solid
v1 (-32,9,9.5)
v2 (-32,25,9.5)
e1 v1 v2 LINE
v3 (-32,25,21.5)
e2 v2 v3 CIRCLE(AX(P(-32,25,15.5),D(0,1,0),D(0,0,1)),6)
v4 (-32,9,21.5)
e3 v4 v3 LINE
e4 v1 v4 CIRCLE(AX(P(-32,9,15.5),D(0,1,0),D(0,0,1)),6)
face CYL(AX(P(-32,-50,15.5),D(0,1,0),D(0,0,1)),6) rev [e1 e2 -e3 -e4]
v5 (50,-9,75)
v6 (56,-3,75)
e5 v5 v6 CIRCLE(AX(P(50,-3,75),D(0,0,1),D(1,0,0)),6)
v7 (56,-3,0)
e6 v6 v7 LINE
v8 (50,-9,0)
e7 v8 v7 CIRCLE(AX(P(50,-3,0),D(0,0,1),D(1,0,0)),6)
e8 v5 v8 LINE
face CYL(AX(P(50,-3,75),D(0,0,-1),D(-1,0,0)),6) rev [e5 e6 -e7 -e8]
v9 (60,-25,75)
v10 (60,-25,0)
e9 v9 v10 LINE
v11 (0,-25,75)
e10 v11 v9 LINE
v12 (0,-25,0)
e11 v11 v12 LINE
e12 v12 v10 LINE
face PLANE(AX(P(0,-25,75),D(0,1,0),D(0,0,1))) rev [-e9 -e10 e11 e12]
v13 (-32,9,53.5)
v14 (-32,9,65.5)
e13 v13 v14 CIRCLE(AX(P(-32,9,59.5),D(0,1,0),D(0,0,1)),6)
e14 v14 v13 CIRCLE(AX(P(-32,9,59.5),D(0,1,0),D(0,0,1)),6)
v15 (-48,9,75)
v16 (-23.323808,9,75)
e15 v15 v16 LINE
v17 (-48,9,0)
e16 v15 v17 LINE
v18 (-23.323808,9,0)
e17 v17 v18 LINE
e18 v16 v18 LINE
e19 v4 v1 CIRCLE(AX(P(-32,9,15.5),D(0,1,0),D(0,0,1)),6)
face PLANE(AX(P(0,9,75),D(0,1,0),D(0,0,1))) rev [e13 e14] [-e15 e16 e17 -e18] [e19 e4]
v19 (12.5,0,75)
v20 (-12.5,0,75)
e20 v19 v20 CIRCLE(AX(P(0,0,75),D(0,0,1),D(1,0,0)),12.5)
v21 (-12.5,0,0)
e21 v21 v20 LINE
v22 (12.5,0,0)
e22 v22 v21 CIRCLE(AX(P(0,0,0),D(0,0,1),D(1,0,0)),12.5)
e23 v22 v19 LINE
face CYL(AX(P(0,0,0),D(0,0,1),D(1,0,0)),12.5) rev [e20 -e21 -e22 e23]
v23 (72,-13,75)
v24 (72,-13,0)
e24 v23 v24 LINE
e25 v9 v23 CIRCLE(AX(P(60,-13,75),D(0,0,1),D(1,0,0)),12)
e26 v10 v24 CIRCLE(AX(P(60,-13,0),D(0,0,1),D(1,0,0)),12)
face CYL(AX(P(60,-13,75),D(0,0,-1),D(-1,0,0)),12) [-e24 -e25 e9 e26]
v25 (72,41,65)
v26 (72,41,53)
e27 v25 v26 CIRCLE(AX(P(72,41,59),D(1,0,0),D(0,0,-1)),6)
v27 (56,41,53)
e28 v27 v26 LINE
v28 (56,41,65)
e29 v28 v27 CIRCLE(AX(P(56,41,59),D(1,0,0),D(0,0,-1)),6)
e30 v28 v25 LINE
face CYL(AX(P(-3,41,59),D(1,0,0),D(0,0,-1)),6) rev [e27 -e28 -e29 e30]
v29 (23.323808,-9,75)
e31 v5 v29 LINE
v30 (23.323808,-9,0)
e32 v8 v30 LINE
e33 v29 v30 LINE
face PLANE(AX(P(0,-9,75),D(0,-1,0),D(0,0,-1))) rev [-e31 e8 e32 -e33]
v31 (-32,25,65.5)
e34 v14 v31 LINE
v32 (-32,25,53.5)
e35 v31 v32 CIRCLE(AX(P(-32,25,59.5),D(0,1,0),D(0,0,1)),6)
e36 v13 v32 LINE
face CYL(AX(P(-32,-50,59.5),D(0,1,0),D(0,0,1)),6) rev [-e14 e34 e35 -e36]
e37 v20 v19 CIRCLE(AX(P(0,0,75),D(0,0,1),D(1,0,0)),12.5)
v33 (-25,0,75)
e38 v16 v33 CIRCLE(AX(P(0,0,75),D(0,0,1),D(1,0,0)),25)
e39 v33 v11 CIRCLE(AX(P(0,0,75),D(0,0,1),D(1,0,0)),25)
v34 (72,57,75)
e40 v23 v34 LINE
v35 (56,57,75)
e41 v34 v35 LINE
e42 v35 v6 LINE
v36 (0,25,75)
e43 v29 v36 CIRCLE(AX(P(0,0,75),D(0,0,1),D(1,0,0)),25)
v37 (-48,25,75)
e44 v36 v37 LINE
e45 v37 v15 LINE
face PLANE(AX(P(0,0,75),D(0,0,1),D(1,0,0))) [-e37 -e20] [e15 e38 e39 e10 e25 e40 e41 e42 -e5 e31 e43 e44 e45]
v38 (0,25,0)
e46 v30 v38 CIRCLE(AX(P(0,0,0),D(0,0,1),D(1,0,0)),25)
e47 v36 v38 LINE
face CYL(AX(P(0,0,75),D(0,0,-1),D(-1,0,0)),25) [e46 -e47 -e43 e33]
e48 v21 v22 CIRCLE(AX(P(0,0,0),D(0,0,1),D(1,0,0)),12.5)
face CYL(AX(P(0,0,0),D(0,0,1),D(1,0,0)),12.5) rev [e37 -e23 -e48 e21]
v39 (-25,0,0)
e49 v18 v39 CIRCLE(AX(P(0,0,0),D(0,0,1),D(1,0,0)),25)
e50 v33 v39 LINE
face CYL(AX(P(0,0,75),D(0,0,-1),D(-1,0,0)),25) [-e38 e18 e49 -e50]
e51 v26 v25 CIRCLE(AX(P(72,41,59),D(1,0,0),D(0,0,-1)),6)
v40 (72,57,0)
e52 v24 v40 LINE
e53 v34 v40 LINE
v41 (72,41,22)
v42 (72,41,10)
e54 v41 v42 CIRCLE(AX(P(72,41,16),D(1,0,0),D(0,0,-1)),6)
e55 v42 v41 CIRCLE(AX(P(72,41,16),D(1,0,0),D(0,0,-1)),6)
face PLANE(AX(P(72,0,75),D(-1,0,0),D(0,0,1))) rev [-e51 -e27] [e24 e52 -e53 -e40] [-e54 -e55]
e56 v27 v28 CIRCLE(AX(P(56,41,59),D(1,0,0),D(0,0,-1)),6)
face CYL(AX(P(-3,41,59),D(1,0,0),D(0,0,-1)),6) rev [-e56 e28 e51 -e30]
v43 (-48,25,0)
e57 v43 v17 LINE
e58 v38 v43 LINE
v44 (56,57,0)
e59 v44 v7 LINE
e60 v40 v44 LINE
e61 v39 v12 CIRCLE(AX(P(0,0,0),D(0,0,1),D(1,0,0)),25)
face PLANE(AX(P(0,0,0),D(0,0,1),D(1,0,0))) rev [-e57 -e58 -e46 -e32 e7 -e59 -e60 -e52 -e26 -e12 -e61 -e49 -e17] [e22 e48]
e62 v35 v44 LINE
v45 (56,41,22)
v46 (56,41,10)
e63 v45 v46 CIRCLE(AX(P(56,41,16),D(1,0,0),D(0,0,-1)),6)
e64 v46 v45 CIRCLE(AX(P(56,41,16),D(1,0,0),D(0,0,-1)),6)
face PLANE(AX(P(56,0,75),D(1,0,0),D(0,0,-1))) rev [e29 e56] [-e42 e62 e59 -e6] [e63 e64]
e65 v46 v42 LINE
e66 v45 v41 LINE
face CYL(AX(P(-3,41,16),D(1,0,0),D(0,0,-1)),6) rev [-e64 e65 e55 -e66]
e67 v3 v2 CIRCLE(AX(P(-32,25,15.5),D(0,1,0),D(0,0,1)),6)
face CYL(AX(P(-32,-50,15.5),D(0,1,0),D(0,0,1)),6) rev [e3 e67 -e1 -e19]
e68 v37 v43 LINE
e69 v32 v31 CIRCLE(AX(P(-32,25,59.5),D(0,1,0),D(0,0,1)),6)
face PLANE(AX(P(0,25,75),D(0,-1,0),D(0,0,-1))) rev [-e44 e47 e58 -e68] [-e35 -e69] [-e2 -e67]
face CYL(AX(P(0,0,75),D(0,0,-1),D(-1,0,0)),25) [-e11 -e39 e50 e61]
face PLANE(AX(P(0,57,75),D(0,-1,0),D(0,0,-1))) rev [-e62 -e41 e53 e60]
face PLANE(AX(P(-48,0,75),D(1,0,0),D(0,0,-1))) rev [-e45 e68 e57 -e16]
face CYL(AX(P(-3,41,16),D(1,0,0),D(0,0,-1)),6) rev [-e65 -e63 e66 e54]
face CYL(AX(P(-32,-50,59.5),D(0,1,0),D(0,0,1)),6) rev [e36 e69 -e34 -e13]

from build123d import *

# Parameters (mm, degrees)
BRACKET_BODY_DEPTH      = 75
FLANGE_A_HOLES_SKETCH_R = 6
FLANGE_A_HOLES_2X_DEPTH = 75
FLANGE_B_HOLES_SKETCH_R = 6
FLANGE_B_HOLES_2X_DEPTH = 75
PIVOT_BORE_SKETCH_R     = 12.5
PIVOT_BORE_DEPTH        = 75


with BuildPart() as part:
    # Bracket Profile Sketch → Bracket Body (new body)
    with BuildSketch(Plane.XY):
        with BuildLine():
            Line((0, -25), (60, -25))
            ThreePointArc((60, -25), (68.485281374, -21.485281374), (72, -13))
            Line((72, -13), (72, 57))
            Line((72, 57), (56, 57))
            Line((56, 57), (56, -3))
            ThreePointArc((56, -3), (54.242640687, -7.242640687), (50, -9))
            Line((50, -9), (23.323807579, -9))
            ThreePointArc((23.323807579, -9), (20.615528128, 14.142135624), (0, 25))
            Line((0, 25), (-48, 25))
            Line((-48, 25), (-48, 9))
            Line((-48, 9), (-23.323807579, 9))
            ThreePointArc((-23.323807579, 9), (-20.615528128, -14.142135624), (0, -25))
        make_face()
    extrude(amount=BRACKET_BODY_DEPTH)

    # Flange A Holes Sketch → Flange A Holes 2x (cut)
    with BuildSketch(Plane(origin=(0, 25, 0), x_dir=(1, 0, 0), z_dir=(0, 1, 0))):
        with Locations(Location((-32, -15.5, 0), (0, 0, 270))):
            Circle(FLANGE_A_HOLES_SKETCH_R)
        with Locations(Location((-32, -59.5, 0), (0, 0, 270))):
            Circle(FLANGE_A_HOLES_SKETCH_R)
    extrude(amount=-FLANGE_A_HOLES_2X_DEPTH, mode=Mode.SUBTRACT)

    # Flange B Holes Sketch → Flange B Holes 2x (cut)
    with BuildSketch(Plane(origin=(72, 0, 0), x_dir=(0, 0, -1), z_dir=(1, 0, 0))):
        with Locations((-59, 41)):
            Circle(FLANGE_B_HOLES_SKETCH_R)
        with Locations((-16, 41)):
            Circle(FLANGE_B_HOLES_SKETCH_R)
    extrude(amount=-FLANGE_B_HOLES_2X_DEPTH, mode=Mode.SUBTRACT)

    # Pivot Bore Sketch → Pivot Bore (cut)
    with BuildSketch(Plane.XY.offset(75)):
        Circle(PIVOT_BORE_SKETCH_R)
    extrude(amount=-PIVOT_BORE_DEPTH, mode=Mode.SUBTRACT)


solid = part.part
